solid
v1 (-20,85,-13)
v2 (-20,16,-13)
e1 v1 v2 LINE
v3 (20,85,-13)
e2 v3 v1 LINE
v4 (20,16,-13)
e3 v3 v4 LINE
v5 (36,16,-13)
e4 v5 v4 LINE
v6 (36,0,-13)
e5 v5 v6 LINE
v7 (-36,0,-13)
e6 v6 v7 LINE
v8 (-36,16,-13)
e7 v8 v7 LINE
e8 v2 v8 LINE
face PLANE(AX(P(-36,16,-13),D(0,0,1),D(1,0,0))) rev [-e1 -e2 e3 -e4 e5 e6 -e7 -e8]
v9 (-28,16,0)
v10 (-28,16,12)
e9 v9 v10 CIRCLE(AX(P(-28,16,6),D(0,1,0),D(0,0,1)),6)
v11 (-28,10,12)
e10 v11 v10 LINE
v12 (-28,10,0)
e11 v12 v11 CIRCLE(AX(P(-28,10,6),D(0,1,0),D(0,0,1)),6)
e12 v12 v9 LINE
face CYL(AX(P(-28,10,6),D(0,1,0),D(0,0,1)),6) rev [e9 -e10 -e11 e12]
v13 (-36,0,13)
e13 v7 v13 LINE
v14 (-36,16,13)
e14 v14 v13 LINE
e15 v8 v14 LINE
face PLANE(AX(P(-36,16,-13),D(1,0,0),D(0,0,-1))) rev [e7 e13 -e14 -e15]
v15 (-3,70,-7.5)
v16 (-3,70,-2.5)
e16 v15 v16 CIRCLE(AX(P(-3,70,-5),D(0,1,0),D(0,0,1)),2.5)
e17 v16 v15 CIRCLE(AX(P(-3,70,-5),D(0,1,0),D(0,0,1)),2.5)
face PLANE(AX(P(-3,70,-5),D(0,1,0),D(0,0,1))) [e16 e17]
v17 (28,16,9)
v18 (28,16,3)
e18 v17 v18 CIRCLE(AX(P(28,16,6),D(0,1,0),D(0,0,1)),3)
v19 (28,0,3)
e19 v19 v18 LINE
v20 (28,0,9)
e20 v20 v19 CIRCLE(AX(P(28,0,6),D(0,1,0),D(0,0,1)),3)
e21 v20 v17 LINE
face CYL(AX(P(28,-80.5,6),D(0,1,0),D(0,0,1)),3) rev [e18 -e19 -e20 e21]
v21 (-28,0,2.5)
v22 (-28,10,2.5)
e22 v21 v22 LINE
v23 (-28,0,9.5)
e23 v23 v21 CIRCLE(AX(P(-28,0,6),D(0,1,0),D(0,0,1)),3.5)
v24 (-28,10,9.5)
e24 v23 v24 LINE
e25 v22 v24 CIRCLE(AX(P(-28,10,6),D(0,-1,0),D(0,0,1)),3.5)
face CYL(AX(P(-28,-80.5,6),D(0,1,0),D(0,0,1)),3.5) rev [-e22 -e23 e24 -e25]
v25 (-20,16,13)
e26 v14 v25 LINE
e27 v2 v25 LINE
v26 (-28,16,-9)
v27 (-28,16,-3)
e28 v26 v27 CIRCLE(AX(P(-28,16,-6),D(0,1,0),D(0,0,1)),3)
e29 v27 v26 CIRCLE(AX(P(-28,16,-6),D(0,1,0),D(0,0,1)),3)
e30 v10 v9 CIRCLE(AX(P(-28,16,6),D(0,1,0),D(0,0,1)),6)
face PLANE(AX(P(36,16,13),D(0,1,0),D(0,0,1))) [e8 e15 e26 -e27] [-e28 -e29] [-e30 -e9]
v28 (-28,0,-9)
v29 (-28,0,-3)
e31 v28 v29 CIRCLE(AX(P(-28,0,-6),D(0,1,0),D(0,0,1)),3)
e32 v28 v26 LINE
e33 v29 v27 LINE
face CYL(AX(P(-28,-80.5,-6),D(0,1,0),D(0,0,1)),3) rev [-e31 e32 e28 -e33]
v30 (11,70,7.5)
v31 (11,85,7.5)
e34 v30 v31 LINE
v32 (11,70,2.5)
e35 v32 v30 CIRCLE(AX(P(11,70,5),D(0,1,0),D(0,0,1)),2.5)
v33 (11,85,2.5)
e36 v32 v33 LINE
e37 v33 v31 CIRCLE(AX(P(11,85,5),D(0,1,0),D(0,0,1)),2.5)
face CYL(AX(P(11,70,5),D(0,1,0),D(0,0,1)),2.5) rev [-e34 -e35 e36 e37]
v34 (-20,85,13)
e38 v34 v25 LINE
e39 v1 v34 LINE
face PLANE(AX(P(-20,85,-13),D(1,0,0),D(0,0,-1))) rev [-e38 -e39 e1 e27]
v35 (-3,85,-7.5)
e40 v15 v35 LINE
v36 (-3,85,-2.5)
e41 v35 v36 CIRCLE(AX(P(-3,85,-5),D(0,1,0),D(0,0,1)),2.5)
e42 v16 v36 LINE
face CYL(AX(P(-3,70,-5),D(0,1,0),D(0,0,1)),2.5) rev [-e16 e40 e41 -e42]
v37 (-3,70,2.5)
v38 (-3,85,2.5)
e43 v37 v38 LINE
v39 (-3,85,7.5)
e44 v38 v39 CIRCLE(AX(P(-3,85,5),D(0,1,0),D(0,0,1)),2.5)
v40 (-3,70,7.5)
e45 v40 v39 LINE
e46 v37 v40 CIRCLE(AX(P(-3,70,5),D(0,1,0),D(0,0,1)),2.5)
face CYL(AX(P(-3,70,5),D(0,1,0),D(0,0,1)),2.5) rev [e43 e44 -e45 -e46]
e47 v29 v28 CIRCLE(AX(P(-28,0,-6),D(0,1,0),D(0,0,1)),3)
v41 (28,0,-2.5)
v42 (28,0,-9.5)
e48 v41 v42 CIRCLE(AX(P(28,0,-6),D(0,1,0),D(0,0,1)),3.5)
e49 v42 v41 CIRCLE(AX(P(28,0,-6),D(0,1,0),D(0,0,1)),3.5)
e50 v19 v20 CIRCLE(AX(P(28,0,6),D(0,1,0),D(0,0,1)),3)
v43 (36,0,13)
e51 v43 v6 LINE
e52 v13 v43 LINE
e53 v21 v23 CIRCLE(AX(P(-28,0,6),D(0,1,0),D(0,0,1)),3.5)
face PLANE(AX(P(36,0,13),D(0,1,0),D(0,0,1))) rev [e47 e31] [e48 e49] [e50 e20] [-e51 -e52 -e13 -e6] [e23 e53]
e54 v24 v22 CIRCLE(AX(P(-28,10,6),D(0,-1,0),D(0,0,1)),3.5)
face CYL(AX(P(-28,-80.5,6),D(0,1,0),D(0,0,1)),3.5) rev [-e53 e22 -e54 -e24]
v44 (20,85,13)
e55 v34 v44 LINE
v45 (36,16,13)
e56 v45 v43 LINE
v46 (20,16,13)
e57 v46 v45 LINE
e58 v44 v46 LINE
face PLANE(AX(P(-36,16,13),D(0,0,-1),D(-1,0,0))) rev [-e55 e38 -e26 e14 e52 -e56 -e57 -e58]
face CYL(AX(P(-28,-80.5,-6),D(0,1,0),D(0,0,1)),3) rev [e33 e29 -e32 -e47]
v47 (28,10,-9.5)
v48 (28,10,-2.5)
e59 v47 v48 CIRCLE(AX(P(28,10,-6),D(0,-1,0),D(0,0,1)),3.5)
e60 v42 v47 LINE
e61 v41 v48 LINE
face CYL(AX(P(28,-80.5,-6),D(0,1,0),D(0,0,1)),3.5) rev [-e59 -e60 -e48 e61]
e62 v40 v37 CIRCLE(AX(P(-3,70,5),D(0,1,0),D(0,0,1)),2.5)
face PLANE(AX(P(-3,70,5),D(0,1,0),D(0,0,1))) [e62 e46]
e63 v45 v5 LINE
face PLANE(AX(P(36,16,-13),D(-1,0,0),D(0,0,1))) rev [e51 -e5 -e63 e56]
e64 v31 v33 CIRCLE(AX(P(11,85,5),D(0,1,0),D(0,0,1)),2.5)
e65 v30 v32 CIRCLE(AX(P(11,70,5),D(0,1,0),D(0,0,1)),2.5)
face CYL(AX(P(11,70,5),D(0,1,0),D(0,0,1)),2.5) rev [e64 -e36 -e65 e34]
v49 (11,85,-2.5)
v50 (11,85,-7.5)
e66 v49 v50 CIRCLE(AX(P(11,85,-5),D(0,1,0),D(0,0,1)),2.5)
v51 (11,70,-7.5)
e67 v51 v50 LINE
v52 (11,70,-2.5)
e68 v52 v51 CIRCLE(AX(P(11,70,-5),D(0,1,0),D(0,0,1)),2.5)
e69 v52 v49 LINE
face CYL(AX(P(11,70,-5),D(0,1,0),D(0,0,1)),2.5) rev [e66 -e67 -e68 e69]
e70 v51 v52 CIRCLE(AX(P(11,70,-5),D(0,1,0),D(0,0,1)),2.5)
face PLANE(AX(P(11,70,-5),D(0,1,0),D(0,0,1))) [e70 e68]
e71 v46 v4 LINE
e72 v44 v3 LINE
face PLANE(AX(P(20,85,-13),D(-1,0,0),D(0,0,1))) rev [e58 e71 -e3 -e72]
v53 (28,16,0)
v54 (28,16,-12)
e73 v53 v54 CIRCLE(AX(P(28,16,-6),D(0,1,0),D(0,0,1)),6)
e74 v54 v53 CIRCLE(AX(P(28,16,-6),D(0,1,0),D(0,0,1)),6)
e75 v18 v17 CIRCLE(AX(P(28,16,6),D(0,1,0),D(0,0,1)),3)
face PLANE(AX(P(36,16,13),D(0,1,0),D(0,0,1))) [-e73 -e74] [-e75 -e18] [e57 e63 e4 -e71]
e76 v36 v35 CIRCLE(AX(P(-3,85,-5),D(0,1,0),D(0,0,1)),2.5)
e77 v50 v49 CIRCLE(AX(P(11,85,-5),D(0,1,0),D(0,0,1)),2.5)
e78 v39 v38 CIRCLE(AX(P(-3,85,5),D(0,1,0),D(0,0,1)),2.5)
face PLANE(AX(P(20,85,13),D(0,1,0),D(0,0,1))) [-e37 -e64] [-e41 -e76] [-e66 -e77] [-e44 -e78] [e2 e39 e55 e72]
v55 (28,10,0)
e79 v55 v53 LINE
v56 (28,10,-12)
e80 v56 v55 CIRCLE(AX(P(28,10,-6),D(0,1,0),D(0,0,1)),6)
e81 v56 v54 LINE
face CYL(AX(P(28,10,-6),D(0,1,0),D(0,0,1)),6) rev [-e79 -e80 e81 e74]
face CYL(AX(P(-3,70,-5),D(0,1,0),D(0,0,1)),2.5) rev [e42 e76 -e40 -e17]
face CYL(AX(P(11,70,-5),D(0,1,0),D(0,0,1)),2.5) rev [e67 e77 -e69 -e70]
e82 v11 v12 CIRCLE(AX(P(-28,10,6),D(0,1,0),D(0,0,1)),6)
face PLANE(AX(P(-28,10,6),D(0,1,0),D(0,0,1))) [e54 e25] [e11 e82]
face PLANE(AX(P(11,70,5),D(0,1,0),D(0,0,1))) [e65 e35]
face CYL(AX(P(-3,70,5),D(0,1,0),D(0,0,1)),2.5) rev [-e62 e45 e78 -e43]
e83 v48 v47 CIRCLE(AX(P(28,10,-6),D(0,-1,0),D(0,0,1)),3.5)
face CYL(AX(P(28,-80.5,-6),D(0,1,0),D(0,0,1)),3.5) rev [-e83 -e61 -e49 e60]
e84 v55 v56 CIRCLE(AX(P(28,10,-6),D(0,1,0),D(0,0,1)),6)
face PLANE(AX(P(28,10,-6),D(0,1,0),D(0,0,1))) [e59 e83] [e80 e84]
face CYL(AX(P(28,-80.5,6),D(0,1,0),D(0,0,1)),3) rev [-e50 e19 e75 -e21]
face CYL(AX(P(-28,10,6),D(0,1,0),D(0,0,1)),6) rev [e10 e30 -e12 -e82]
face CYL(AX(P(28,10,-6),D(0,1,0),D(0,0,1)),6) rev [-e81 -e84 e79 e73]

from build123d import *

# Parameters (mm, degrees)
SKETCH1_W           = 72
SKETCH1_H           = 26
BOSS_EXTRUDE1_DEPTH = 16
SKETCH2_W           = 40
SKETCH2_H           = 26
BOSS_EXTRUDE2_DEPTH = 69
SKETCH3_R           = 3.5
SKETCH3_R_2         = 3
CUT_EXTRUDE1_DEPTH  = 96.5
SKETCH4_R           = 6
CUT_EXTRUDE2_DEPTH  = 6
SKETCH5_R           = 2.5
CUT_EXTRUDE3_DEPTH  = 15


with BuildPart() as part:
    # Sketch1 → Boss-Extrude1 (new body)
    with BuildSketch(Plane(origin=(0, 0, 0), x_dir=(1, 0, 0), z_dir=(0, 1, 0))):
        Rectangle(SKETCH1_W, SKETCH1_H)
    extrude(amount=BOSS_EXTRUDE1_DEPTH)

    # Sketch2 → Boss-Extrude2 (add)
    with BuildSketch(Plane(origin=(0, 16, 0), x_dir=(1, 0, 0), z_dir=(0, 1, 0))):
        Rectangle(SKETCH2_W, SKETCH2_H)
    extrude(amount=BOSS_EXTRUDE2_DEPTH)

    # Sketch3 → Cut-Extrude1 (cut)
    with BuildSketch(Plane(origin=(0, 16, 0), x_dir=(1, 0, 0), z_dir=(0, 1, 0))):
        with Locations(Location((28, 6, 0), (0, 0, 270))):
            Circle(SKETCH3_R)
        with Locations(Location((28, -6, 0), (0, 0, 270))):
            Circle(SKETCH3_R_2)
        with Locations(Location((-28, -6, 0), (0, 0, 270))):
            Circle(SKETCH3_R)
        with Locations(Location((-28, 6, 0), (0, 0, 270))):
            Circle(SKETCH3_R_2)
    extrude(amount=-CUT_EXTRUDE1_DEPTH, mode=Mode.SUBTRACT)

    # Sketch4 → Cut-Extrude2 (cut)
    with BuildSketch(Plane(origin=(0, 16, 0), x_dir=(1, 0, 0), z_dir=(0, 1, 0))):
        with Locations(Location((28, 6, 0), (0, 0, 270))):
            Circle(SKETCH4_R)
        with Locations(Location((-28, -6, 0), (0, 0, 270))):
            Circle(SKETCH4_R)
    extrude(amount=-CUT_EXTRUDE2_DEPTH, mode=Mode.SUBTRACT)

    # Sketch5 → Cut-Extrude3 (cut)
    with BuildSketch(Plane(origin=(0, 85, 0), x_dir=(1, 0, 0), z_dir=(0, 1, 0))):
        with Locations(Location((-3, 5, 0), (0, 0, 270))):
            Circle(SKETCH5_R)
        with Locations(Location((11, 5, 0), (0, 0, 270))):
            Circle(SKETCH5_R)
        with Locations(Location((11, -5, 0), (0, 0, 270))):
            Circle(SKETCH5_R)
        with Locations(Location((-3, -5, 0), (0, 0, 270))):
            Circle(SKETCH5_R)
    extrude(amount=-CUT_EXTRUDE3_DEPTH, mode=Mode.SUBTRACT)


solid = part.part
